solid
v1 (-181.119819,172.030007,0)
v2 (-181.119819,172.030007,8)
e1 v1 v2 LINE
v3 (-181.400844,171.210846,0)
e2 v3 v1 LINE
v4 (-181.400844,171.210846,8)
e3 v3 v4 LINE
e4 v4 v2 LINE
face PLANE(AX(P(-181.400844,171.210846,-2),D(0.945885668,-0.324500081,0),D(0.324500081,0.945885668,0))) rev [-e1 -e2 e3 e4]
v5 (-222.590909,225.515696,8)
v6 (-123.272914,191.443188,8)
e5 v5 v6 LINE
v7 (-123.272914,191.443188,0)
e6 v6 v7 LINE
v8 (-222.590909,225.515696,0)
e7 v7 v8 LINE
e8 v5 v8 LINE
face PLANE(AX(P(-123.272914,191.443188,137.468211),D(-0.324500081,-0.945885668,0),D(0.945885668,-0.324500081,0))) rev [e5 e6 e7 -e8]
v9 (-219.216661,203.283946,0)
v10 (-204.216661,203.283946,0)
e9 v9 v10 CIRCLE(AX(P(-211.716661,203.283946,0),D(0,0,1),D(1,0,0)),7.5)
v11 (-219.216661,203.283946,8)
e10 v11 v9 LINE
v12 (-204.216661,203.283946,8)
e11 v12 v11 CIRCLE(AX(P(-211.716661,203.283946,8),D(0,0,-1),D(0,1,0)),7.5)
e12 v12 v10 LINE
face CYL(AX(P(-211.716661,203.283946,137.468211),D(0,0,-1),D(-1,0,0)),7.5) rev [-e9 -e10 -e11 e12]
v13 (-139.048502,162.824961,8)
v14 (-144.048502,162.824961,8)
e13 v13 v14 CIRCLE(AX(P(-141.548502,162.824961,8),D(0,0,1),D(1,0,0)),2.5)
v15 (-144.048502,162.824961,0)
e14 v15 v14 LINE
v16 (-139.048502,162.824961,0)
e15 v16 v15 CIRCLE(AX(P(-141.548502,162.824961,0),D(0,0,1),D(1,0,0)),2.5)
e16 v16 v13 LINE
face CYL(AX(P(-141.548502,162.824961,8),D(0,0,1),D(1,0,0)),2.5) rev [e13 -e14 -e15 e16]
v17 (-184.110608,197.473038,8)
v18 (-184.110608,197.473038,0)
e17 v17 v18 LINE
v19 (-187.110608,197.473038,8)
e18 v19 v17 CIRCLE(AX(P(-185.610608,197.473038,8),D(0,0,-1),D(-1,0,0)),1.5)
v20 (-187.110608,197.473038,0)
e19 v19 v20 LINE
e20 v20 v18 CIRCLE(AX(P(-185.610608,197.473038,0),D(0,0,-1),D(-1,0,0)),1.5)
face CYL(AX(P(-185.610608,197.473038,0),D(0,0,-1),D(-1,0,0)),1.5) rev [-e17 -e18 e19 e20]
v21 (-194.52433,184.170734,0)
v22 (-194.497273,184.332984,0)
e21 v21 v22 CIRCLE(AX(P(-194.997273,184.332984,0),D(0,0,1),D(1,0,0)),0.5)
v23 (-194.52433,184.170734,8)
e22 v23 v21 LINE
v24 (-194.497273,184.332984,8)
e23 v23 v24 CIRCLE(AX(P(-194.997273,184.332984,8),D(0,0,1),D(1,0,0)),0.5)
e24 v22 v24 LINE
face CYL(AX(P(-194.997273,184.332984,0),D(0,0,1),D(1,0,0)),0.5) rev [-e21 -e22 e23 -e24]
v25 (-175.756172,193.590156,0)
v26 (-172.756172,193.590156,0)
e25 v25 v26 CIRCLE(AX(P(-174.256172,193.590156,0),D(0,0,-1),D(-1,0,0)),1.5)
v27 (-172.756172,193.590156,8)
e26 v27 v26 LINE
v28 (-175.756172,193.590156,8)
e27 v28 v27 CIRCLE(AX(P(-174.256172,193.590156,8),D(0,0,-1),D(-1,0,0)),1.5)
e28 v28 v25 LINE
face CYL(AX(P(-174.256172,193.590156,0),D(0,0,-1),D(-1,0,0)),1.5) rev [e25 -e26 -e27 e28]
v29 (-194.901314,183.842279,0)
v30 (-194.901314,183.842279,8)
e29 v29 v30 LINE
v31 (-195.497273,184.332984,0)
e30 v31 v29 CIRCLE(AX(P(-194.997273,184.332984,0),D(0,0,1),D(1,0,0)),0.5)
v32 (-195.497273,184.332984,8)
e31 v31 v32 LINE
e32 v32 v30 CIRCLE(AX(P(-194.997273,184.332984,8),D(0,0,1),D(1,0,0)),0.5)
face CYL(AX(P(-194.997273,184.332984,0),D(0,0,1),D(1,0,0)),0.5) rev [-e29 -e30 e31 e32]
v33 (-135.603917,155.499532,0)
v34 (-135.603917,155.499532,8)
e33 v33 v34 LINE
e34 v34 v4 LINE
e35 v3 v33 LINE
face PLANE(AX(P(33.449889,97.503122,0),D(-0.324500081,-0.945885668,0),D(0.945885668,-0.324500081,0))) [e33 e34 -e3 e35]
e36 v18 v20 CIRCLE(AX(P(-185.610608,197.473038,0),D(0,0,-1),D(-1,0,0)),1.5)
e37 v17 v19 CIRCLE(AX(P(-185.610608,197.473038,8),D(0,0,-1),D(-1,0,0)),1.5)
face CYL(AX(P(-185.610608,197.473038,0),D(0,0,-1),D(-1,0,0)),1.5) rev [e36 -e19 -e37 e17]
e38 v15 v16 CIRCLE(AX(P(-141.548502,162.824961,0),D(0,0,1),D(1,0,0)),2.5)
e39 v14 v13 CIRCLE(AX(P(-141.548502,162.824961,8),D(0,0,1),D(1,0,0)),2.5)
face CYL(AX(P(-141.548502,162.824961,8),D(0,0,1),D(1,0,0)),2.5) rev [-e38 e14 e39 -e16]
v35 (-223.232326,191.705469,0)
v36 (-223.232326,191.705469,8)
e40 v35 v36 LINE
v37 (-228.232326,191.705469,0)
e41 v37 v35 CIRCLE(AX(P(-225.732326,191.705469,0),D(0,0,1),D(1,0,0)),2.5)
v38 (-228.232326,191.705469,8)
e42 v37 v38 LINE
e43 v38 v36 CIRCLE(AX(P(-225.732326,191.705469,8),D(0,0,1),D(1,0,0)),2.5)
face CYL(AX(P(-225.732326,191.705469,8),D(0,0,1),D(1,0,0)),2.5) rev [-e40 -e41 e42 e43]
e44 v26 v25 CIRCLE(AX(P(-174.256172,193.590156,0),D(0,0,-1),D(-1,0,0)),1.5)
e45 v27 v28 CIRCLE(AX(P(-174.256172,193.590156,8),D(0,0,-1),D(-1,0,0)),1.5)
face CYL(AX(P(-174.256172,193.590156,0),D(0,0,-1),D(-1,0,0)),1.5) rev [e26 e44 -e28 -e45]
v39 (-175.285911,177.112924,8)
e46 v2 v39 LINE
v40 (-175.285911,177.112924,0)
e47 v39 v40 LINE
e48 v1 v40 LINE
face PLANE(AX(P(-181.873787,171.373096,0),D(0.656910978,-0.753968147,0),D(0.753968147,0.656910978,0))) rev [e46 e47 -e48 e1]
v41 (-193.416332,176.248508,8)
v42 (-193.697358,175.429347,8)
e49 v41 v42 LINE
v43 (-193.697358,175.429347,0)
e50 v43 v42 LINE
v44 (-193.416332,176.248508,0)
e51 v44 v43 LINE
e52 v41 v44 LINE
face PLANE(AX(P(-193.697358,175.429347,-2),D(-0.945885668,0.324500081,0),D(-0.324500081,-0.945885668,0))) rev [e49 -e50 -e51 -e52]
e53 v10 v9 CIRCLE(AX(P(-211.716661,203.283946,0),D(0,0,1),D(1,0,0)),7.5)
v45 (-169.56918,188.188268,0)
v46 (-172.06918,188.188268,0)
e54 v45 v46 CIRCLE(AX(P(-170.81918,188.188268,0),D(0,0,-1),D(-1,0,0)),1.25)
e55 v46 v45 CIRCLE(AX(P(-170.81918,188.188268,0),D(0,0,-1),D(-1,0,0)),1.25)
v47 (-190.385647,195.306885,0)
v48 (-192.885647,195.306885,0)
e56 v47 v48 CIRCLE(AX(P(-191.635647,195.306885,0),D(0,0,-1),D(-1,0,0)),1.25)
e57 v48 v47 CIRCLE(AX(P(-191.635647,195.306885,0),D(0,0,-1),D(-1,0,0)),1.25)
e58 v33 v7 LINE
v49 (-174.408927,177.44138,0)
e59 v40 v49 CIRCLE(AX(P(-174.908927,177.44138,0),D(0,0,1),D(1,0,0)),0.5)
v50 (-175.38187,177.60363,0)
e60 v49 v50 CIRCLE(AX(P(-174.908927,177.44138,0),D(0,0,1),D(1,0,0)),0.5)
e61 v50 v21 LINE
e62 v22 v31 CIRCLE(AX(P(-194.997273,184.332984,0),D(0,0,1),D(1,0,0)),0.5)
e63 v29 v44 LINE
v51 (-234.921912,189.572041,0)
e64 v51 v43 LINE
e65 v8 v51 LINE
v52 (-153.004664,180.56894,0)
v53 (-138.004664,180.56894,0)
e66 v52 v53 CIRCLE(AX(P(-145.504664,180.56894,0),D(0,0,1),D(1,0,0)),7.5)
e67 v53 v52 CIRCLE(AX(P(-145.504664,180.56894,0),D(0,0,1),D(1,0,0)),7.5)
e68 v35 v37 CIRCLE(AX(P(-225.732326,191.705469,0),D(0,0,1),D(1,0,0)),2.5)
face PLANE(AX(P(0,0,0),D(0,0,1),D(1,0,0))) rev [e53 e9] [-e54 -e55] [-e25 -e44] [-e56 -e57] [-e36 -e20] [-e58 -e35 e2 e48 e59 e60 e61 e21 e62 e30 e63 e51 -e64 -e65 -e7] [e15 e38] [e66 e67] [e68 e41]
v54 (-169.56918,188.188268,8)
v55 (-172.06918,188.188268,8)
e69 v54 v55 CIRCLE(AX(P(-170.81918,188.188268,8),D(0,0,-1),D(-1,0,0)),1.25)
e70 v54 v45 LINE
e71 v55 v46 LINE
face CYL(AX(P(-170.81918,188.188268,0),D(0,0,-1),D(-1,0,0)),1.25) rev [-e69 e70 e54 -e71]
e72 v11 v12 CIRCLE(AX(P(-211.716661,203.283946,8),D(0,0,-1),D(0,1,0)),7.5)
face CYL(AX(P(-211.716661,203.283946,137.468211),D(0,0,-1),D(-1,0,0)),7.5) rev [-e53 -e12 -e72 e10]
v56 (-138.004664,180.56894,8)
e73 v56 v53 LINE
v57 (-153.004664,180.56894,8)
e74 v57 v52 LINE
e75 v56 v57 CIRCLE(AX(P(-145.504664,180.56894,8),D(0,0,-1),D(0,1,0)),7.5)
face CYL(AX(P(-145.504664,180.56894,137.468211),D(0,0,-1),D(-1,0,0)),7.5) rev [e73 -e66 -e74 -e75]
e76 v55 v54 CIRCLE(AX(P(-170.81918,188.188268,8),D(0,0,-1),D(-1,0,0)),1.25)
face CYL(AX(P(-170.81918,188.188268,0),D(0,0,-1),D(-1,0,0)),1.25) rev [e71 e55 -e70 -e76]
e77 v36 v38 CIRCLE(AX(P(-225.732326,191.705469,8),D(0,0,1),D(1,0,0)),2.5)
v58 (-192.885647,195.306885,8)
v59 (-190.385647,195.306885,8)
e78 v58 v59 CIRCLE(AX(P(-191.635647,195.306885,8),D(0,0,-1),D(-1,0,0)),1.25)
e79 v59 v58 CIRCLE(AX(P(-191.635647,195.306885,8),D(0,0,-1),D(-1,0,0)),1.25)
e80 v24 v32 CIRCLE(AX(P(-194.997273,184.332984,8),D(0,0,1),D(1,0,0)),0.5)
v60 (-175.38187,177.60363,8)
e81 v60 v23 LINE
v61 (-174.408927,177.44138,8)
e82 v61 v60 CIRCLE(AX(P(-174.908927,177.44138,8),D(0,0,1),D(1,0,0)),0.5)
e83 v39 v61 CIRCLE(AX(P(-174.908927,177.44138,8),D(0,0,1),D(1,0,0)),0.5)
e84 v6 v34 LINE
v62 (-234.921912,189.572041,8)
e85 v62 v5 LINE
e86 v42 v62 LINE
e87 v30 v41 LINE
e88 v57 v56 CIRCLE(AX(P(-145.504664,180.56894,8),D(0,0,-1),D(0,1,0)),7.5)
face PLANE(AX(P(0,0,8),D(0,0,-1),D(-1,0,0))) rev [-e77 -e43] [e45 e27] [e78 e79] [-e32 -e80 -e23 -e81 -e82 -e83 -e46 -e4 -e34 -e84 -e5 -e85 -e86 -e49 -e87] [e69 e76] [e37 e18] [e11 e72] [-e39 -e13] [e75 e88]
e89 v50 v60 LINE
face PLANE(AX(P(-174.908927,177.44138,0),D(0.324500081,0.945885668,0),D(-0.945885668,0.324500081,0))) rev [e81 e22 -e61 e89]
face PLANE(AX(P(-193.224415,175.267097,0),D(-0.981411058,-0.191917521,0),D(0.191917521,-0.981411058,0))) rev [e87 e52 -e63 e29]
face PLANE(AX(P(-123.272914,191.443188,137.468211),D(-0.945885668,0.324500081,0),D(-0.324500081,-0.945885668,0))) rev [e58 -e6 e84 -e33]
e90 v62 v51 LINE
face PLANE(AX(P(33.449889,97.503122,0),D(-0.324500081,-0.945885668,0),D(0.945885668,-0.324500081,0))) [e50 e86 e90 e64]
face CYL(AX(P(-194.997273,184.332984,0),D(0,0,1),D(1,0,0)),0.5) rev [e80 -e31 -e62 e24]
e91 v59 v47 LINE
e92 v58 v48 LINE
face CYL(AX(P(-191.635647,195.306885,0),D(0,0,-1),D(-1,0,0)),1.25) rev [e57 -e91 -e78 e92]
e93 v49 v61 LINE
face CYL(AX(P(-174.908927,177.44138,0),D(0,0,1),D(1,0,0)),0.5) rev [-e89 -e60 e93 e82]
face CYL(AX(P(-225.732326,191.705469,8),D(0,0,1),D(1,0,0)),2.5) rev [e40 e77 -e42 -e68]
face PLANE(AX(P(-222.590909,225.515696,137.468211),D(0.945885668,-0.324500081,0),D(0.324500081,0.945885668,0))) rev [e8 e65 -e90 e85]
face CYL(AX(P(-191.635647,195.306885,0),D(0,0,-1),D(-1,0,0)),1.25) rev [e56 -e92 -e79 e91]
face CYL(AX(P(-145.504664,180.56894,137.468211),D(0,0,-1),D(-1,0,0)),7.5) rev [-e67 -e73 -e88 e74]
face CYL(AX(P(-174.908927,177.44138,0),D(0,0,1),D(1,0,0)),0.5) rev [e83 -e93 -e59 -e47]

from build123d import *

# Parameters (mm, degrees)
SKETCH_1_R             = 7.5
EXTRUDE_1_DEPTH        = 8
SKETCH_2_W             = 105
SKETCH_2_H             = 8
EXTRUDE_2_DEPTH        = 3
CUT_EXTRUDE_1_DEPTH    = 326.744737494
HOLE_WIZARD_M6_1_D     = 5
HOLE_WIZARD_M6_1_DEPTH = 15
HOLE_WIZARD_M6_1_TIP   = 1.502151548
HOLE_WIZARD_M3_1_D     = 2.5
MM_1_D                 = 3
CUT_EXTRUDE_2_DEPTH    = 10
SKETCH_14_R            = 0.5
CUT_EXTRUDE_3_DEPTH    = 326.744737494


with BuildPart() as part:
    # 草图1 → 凸台-拉伸1 (new body)
    with BuildSketch(Plane.XY):
        Polygon((-123.272913695, 191.443187885), (-134.630416513, 158.337189489), (-233.948411698, 192.409697944), (-222.59090888, 225.515696339), align=None)
        with Locations(Location((-211.716661092, 203.283945733, 0), (0, 0, 90))):
            Circle(SKETCH_1_R, mode=Mode.SUBTRACT)
        with Locations(Location((-145.504664302, 180.568940096, 0), (0, 0, 90))):
            Circle(SKETCH_1_R, mode=Mode.SUBTRACT)
    extrude(amount=EXTRUDE_1_DEPTH)

    # 草图2 → 凸台-拉伸2 (add)
    with BuildSketch(Plane(origin=(34.423389522, 100.340778821, 0), x_dir=(0.9458856684293921, -0.3245000805236912, 0), z_dir=(-0.3245000805236912, -0.9458856684293921, 0))):
        with Locations((-231.225412254, 4)):
            Rectangle(SKETCH_2_W, SKETCH_2_H)
    extrude(amount=EXTRUDE_2_DEPTH)

    # 草图3 → 切除-拉伸1 (cut, through all)
    with BuildSketch(Plane.XY.offset(8)):
        Polygon((-181.873786677, 171.373096295), (-193.224414699, 175.267097261), (-194.997272817, 184.33298428), (-174.908927271, 177.441379972), align=None)
    extrude(amount=-CUT_EXTRUDE_1_DEPTH, mode=Mode.SUBTRACT)

    # M6 螺纹孔1
    with Locations(Plane.XY.offset(8)):
        with Locations((-141.5485017, 162.824961471), (-225.73232619, 191.705468637)):
            Hole(HOLE_WIZARD_M6_1_D / 2, depth=HOLE_WIZARD_M6_1_DEPTH)
            with Locations((0, 0, -(HOLE_WIZARD_M6_1_DEPTH + HOLE_WIZARD_M6_1_TIP / 2))):  # 118° drill point
                Cone(0, HOLE_WIZARD_M6_1_D / 2, HOLE_WIZARD_M6_1_TIP, mode=Mode.SUBTRACT)

    # M3 螺纹孔1 (through all)
    with Locations(Plane(origin=(0, 0, 0), x_dir=(-1, 0, 0), z_dir=(0, 0, -1))):
        with Locations((170.819179959, 188.188267601), (191.635646748, 195.306884773)):
            Hole(HOLE_WIZARD_M3_1_D / 2)

    # 大小mm 暗销孔1 (through all)
    with Locations(Plane(origin=(0, 0, 0), x_dir=(-1, 0, 0), z_dir=(0, 0, -1))):
        with Locations((174.256171582, 193.590156353), (185.610608012, 197.473038447)):
            Hole(MM_1_D / 2)

    # 草图13 → 切除-拉伸2 (cut)
    with BuildSketch(Plane.XY.offset(8)):
        Polygon((-193.697357533, 175.429347302), (-192.732083432, 178.243025921), (-180.825057933, 172.889205286), (-181.400843843, 171.210846255), align=None)
    extrude(amount=-CUT_EXTRUDE_2_DEPTH, mode=Mode.SUBTRACT)

    # 草图14 → 切除-拉伸3 (cut, through all)
    with BuildSketch(Plane.XY.offset(8)):
        with Locations((-194.997272817, 184.33298428)):
            Circle(SKETCH_14_R)
        with Locations((-174.908927271, 177.441379972)):
            Circle(SKETCH_14_R)
    extrude(amount=-CUT_EXTRUDE_3_DEPTH, mode=Mode.SUBTRACT)


solid = part.part
